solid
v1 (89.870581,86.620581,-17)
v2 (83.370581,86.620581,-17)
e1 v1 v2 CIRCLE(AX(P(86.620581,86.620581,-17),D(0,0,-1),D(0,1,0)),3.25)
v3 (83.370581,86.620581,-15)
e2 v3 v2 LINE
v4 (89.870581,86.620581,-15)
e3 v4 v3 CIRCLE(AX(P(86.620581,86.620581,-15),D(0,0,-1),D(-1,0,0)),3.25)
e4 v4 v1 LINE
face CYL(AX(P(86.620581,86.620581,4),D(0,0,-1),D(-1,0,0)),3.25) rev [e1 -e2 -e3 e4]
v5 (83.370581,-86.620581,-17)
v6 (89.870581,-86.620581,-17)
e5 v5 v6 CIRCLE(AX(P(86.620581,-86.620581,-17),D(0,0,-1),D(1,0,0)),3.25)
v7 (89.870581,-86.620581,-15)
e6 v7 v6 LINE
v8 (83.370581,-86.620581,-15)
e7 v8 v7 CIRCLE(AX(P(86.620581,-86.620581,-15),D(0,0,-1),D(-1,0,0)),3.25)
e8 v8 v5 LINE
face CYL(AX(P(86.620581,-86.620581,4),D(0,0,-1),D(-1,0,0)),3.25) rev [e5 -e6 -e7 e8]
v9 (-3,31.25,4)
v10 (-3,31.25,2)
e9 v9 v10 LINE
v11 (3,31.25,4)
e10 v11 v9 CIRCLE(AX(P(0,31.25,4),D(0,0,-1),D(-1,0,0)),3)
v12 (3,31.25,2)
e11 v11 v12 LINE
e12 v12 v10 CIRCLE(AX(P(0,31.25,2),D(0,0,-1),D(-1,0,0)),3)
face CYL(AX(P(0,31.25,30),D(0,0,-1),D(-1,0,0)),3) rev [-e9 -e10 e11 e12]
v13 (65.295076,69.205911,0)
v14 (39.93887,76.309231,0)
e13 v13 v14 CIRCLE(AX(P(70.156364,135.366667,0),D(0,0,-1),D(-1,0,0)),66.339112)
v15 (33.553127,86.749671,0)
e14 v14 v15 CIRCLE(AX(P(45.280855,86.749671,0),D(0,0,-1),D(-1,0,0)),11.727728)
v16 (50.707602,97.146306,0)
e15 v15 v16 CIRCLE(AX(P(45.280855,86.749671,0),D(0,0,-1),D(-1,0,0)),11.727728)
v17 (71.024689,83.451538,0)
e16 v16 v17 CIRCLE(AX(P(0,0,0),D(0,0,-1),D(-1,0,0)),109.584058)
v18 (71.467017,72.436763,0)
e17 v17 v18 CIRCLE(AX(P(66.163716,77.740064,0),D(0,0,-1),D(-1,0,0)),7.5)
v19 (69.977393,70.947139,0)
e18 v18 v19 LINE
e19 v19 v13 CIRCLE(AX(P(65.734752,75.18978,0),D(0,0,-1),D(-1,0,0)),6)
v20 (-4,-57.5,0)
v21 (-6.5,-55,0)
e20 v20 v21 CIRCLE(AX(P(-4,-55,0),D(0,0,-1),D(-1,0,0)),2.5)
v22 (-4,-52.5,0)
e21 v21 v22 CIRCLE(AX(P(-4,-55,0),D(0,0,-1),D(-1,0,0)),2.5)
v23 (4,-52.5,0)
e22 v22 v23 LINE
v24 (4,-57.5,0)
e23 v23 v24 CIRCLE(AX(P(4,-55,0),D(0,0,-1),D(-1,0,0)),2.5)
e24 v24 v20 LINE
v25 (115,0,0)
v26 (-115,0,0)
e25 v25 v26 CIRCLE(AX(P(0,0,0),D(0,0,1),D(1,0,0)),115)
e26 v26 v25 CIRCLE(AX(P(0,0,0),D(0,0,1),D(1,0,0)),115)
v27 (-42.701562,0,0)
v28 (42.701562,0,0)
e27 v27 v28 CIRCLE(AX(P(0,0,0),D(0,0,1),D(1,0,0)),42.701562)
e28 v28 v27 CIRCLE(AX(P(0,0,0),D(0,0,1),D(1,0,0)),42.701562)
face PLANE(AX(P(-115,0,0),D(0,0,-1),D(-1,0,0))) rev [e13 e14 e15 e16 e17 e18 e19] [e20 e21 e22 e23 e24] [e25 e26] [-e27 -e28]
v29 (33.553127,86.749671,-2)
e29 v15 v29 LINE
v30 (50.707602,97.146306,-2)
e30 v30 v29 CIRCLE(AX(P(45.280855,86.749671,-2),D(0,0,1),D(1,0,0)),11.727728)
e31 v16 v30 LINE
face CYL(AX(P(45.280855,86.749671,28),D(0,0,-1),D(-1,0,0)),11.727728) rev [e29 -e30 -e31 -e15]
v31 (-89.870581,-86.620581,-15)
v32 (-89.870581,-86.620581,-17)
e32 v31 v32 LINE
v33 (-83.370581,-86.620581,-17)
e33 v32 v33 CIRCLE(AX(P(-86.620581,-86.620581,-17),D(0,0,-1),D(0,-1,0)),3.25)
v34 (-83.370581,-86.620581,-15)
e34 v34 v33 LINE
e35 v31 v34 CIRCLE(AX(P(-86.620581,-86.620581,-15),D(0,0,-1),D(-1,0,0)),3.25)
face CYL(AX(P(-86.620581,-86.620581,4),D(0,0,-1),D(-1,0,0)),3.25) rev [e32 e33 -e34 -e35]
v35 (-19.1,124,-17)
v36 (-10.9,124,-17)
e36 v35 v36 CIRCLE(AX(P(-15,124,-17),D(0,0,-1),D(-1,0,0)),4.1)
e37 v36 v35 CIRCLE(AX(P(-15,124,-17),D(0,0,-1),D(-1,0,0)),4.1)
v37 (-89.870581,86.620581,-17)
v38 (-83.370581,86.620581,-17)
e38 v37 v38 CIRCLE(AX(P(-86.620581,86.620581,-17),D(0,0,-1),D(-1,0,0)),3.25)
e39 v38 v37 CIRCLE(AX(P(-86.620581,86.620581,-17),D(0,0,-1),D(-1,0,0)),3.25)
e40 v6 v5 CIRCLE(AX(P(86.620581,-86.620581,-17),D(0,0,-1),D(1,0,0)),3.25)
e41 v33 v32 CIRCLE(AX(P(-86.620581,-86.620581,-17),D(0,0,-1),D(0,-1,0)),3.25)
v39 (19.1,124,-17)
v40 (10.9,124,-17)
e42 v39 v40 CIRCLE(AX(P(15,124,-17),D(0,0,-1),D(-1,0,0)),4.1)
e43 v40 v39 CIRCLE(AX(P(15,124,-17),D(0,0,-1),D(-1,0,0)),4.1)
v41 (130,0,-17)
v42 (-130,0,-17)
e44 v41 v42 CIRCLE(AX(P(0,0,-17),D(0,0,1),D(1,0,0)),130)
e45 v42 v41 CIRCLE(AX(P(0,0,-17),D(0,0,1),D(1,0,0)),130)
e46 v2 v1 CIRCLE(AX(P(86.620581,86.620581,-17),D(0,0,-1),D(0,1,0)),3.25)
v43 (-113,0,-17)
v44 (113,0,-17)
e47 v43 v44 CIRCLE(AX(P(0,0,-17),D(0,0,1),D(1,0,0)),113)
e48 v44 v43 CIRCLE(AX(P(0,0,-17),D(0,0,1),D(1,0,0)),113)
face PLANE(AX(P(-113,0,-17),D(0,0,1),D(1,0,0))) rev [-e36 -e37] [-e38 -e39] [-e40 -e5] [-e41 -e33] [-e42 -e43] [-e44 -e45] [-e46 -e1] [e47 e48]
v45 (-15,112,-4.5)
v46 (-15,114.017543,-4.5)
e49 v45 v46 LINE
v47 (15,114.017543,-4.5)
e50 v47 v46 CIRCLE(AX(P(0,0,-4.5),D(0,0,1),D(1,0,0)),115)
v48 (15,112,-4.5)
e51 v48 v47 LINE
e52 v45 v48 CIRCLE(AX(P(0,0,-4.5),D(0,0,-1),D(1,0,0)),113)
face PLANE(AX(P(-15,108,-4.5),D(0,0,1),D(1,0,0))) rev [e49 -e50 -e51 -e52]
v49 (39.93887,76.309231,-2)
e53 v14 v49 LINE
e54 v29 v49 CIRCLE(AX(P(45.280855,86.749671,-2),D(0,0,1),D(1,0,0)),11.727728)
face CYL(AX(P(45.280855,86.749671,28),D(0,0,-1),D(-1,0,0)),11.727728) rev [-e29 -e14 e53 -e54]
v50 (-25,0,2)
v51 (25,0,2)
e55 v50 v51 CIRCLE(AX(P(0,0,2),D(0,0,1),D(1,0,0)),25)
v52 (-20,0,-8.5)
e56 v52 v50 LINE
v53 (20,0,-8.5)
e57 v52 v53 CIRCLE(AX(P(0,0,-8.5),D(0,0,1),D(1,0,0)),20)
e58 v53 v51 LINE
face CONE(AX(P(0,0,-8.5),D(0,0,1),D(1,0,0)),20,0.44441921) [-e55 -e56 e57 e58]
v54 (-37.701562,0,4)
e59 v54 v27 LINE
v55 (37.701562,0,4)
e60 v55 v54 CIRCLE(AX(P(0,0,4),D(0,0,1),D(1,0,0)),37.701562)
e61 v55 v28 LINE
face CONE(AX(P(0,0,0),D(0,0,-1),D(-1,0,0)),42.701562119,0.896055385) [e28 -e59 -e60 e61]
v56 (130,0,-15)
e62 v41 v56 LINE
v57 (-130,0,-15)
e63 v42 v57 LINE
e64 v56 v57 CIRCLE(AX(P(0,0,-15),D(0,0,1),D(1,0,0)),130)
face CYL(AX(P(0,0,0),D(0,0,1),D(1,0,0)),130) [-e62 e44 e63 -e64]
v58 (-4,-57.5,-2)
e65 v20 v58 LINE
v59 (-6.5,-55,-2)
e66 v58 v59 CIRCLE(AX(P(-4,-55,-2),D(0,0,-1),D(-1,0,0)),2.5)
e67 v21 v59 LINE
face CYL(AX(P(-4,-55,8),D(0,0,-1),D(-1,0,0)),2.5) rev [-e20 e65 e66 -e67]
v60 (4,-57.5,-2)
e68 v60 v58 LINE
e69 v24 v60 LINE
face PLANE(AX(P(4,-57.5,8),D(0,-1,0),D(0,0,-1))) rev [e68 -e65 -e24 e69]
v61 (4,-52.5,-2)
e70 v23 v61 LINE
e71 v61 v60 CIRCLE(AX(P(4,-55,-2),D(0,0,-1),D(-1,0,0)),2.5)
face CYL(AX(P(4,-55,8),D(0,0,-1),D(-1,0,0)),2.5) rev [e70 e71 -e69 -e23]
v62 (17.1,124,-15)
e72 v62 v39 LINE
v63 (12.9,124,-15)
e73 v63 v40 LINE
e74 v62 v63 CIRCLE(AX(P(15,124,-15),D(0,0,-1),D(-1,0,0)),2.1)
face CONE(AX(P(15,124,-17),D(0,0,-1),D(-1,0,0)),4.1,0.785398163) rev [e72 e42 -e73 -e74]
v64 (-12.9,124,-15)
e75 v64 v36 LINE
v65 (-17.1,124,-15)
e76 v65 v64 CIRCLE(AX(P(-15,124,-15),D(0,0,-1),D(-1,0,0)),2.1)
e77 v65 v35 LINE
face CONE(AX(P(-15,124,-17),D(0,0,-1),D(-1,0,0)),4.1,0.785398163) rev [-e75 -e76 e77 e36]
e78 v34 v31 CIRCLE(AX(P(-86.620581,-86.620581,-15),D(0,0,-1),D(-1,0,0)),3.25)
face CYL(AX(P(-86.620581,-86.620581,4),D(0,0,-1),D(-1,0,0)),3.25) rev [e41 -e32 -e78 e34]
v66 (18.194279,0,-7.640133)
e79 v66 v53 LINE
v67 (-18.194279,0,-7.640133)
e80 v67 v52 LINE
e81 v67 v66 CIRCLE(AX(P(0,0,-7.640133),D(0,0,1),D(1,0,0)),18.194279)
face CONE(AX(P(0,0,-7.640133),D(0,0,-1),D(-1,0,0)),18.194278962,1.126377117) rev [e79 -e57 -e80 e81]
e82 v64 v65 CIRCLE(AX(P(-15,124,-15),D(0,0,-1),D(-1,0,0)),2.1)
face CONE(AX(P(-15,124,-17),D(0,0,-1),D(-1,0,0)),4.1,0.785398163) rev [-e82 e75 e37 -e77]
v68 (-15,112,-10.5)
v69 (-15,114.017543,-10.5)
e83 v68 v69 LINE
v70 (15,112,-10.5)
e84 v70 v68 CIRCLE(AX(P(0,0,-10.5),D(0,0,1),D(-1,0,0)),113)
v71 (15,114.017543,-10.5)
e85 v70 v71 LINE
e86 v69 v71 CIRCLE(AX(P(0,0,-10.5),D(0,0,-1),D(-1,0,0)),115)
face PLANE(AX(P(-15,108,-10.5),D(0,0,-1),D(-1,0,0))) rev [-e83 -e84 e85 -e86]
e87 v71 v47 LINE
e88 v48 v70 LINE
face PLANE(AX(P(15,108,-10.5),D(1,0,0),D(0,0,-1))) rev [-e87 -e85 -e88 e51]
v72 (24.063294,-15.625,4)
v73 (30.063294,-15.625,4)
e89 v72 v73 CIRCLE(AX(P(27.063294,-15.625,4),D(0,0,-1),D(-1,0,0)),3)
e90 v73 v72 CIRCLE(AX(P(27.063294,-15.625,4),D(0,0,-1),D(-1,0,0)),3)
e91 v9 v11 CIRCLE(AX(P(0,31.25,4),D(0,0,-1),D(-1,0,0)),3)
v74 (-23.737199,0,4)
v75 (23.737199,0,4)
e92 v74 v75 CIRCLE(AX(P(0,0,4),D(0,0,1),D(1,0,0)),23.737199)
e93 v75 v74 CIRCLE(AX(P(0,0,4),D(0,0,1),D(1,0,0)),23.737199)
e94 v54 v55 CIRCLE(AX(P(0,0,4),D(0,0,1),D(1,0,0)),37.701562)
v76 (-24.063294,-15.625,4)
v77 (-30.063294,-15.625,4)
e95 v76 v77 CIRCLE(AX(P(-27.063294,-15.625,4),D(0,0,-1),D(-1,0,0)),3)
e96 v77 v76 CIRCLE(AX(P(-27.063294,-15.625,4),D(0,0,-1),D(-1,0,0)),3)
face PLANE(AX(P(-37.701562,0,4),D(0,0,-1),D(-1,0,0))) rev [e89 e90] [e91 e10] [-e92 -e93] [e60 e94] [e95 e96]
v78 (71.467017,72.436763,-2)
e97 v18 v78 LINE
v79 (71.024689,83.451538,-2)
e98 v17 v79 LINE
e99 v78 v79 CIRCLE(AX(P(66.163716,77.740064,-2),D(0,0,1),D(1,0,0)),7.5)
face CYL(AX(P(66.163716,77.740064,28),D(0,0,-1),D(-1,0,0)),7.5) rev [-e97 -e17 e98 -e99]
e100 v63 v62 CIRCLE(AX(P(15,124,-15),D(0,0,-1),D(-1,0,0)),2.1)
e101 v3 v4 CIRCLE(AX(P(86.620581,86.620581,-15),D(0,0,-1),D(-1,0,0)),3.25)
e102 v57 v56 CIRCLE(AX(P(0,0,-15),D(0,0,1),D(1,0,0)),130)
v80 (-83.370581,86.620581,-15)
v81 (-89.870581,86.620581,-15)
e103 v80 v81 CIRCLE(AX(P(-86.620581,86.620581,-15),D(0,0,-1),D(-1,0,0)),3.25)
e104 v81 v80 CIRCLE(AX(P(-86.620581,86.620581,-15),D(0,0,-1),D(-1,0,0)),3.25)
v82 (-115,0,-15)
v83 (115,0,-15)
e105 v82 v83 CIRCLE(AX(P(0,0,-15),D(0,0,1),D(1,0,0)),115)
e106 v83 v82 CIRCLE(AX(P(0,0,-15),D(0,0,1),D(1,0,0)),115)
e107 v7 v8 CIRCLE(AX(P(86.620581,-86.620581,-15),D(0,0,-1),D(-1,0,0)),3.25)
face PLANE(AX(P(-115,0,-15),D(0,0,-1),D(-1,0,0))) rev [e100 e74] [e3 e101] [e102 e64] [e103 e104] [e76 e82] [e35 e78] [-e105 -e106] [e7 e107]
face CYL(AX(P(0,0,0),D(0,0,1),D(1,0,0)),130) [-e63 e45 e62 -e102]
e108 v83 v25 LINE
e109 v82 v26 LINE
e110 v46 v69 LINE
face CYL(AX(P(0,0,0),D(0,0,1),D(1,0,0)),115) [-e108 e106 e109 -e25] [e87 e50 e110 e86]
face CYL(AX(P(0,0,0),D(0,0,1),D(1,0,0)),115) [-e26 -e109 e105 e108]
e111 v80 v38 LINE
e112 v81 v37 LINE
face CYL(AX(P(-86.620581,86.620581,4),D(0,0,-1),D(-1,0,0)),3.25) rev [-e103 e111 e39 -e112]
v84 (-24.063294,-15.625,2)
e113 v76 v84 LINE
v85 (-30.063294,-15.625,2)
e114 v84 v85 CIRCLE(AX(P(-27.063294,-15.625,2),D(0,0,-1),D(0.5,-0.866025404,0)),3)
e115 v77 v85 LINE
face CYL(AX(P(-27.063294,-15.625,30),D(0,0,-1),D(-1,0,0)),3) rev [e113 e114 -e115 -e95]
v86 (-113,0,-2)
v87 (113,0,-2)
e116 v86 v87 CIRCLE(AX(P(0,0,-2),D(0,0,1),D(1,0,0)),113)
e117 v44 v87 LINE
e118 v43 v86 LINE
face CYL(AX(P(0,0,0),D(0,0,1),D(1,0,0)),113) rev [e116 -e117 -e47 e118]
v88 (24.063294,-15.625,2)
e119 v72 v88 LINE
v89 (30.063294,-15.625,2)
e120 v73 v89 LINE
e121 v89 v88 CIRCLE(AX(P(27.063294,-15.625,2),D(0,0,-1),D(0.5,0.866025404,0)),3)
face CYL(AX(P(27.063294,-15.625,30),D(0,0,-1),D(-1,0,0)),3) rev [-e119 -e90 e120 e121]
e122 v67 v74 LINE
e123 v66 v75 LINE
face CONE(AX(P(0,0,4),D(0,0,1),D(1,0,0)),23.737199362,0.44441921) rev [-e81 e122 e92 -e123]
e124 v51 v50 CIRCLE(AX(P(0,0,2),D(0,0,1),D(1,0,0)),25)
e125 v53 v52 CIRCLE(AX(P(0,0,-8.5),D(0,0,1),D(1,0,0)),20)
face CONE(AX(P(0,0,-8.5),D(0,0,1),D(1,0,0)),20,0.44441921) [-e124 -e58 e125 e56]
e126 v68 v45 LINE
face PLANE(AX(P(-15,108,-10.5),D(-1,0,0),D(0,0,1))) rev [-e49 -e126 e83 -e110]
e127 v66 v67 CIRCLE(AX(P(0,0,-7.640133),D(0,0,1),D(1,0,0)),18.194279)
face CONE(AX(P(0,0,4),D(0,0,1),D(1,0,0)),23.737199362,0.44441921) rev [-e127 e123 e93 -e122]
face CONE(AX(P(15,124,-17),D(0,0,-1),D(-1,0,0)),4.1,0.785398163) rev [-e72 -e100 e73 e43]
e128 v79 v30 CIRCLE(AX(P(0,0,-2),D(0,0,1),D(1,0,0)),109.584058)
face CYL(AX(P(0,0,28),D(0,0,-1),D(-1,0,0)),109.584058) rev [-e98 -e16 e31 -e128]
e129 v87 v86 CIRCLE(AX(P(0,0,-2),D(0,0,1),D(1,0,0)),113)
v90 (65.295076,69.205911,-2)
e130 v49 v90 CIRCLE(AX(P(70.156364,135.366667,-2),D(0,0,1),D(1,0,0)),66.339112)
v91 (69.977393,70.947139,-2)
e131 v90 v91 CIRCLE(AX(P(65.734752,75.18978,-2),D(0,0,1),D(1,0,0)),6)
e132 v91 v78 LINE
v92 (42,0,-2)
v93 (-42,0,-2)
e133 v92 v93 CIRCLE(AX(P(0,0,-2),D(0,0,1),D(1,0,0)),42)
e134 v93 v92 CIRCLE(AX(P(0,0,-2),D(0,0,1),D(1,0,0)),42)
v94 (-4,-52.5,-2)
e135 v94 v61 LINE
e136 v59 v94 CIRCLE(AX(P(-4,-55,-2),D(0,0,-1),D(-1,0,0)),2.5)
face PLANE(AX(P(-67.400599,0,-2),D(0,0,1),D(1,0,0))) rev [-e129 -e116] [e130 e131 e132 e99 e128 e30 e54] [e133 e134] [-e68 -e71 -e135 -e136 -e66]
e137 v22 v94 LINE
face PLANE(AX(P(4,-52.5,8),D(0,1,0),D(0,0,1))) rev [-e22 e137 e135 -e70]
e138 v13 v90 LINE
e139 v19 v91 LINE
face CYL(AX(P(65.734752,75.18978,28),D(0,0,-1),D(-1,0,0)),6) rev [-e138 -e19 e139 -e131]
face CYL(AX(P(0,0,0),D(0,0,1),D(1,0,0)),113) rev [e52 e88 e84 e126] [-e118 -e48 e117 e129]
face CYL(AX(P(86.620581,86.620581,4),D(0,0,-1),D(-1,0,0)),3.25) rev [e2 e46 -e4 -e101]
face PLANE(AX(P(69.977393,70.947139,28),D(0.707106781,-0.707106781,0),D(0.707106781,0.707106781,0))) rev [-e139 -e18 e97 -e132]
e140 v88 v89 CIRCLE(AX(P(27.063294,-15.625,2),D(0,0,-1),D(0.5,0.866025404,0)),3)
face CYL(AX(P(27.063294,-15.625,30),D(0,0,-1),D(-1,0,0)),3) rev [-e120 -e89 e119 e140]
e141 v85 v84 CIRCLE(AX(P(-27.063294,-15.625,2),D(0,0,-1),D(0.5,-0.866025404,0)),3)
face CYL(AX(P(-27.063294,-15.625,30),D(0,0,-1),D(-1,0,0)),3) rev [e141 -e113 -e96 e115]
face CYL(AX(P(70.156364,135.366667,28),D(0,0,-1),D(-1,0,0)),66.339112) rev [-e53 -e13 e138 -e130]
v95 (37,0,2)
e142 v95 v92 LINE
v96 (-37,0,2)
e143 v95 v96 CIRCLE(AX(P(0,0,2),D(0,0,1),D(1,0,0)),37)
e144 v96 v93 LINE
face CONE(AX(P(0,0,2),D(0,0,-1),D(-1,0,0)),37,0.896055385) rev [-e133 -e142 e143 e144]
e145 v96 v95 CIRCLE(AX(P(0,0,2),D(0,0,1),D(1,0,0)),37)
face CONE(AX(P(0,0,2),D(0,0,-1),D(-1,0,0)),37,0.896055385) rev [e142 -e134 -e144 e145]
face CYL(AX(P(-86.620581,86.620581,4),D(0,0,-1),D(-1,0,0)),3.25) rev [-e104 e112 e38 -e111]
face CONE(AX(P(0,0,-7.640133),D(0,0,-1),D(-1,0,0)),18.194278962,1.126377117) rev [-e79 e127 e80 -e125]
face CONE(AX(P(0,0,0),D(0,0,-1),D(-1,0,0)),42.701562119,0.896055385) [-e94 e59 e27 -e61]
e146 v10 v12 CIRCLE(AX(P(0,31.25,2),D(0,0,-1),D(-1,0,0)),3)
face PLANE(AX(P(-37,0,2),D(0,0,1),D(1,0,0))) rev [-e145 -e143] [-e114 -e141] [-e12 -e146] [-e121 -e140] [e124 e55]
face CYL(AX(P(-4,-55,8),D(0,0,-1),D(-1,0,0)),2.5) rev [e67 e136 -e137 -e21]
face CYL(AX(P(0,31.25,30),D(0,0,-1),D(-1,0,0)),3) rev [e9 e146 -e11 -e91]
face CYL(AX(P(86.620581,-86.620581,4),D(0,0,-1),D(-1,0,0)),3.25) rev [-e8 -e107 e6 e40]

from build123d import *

# Parameters (mm, degrees)
CUT_EXTRUDE1_DEPTH                                   = 45
CUT_EXTRUDE2_DEPTH                                   = 10
SKETCH5_W                                            = 30
SKETCH5_H                                            = 6
CUT_EXTRUDE3_DEPTH                                   = 32
HOLE_SIZE_BY_CROSS_RECESS_COUNTERSUNK_SE_D           = 3.7
HOLE_SIZE_BY_CROSS_RECESS_COUNTERSUNK_SE_CSINK_D     = 8.2
HOLE_SIZE_BY_CROSS_RECESS_COUNTERSUNK_SE_CSINK_ANGLE = 90
SKETCH8_R                                            = 3.25
CUT_EXTRUDE4_DEPTH                                   = 186.04323819
CIRPATTERN1_COUNT                                    = 4
SKETCH9_R                                            = 3
CUT_EXTRUDE5_DEPTH                                   = 28
CIRPATTERN2_COUNT                                    = 3


with BuildPart() as part:
    # Sketch1 → Revolve1 (revolve)
    with BuildSketch(Plane(origin=(0, 0, 0), x_dir=(1, 0, 0), z_dir=(0, 1, 0)), mode=Mode.PRIVATE) as revolve1_sk:
        Polygon((-115, 15), (-130, 15), (-130, 17), (-113, 17), (-113, 2), (-67.400598844, 2), (-42, 2), (-37, -2), (-25, -2), (-20, 8.5), (-18.194278962, 7.640132839), (-23.737199362, -4), (-37.701562119, -4), (-42.701562119, 0), (-115, 0), align=None)
    revolve(revolve1_sk.sketch.rotate(Axis((0, 0, 0), (0, 0, -1)), 180), axis=Axis((0, 0, 0), (0, 0, -1)))

    # Sketch3 → Cut-Extrude1 (cut)
    with BuildSketch(Plane(origin=(0, 0, -17), x_dir=(-1, 0, 0), z_dir=(0, 0, -1))):
        with BuildLine():
            Line((-69.977392836, 70.947139279), (-71.467016668, 72.43676311))
            ThreePointArc((-71.467016668, 72.43676311), (-73.65767572, 78.041003905), (-71.024689008, 83.451538346))
            ThreePointArc((-71.024689008, 83.451538346), (-61.250096658, 90.868538892), (-50.7076021, 97.146306107))
            ThreePointArc((-50.7076021, 97.146306107), (-34.862231231, 92.134081811), (-39.938869953, 76.309230795))
            ThreePointArc((-39.938869953, 76.309230795), (-52.260986787, 71.486832981), (-65.295075938, 69.205911249))
            ThreePointArc((-65.295075938, 69.205911249), (-67.826068353, 69.566044861), (-69.977392836, 70.947139279))
        make_face()
    extrude(amount=-CUT_EXTRUDE1_DEPTH, mode=Mode.SUBTRACT)

    # Sketch4 → Cut-Extrude2 (cut)
    with BuildSketch(Plane(origin=(0, 0, -2), x_dir=(-1, 0, 0), z_dir=(0, 0, -1))):
        with BuildLine():
            Line((-4, -52.5), (4, -52.5))
            ThreePointArc((4, -52.5), (6.5, -55), (4, -57.5))
            Line((4, -57.5), (-4, -57.5))
            ThreePointArc((-4, -57.5), (-6.5, -55), (-4, -52.5))
        make_face()
    extrude(amount=-CUT_EXTRUDE2_DEPTH, mode=Mode.SUBTRACT)

    # Sketch5 → Cut-Extrude3 (cut)
    with BuildSketch(Plane(origin=(0, 140, 0), x_dir=(1, 0, 0), z_dir=(0, 1, 0))):
        with Locations((0, 7.5)):
            Rectangle(SKETCH5_W, SKETCH5_H)
    extrude(amount=-CUT_EXTRUDE3_DEPTH, mode=Mode.SUBTRACT)

    # Hole size by cross-recess countersunk self-tapping screw type1 (through all)
    with Locations(Plane(origin=(15, 124, -17), x_dir=(-1, 0, 0), z_dir=(0, 0, -1))):
        with Locations((0, 0), (30, 0)):
            CounterSinkHole(HOLE_SIZE_BY_CROSS_RECESS_COUNTERSUNK_SE_D / 2, HOLE_SIZE_BY_CROSS_RECESS_COUNTERSUNK_SE_CSINK_D / 2, counter_sink_angle=HOLE_SIZE_BY_CROSS_RECESS_COUNTERSUNK_SE_CSINK_ANGLE)

    # Sketch8 → Cut-Extrude4 (cut, through all)
    with BuildSketch(Plane(origin=(0, 0, -17), x_dir=(-1, 0, 0), z_dir=(0, 0, -1))):
        with Locations((86.620580695, 86.620580695)):
            Circle(SKETCH8_R)
    cut_extrude4 = extrude(amount=-CUT_EXTRUDE4_DEPTH, mode=Mode.SUBTRACT)

    # CirPattern1: Cut-Extrude4 ×4 about axis
    cirpattern1_axis = Axis((0, 0, 0), (0, 0, 1))
    for i in range(1, CIRPATTERN1_COUNT):
        add(cut_extrude4.rotate(cirpattern1_axis, i * 360 / CIRPATTERN1_COUNT), mode=Mode.SUBTRACT)

    # Sketch9 → Cut-Extrude5 (cut)
    with BuildSketch(Plane(origin=(0, 0, 2), x_dir=(-1, 0, 0), z_dir=(0, 0, -1))):
        with Locations((0, 31.25)):
            Circle(SKETCH9_R)
    cut_extrude5 = extrude(amount=-CUT_EXTRUDE5_DEPTH, mode=Mode.SUBTRACT)

    # CirPattern2: Cut-Extrude5 ×3 about axis
    cirpattern2_axis = Axis((0, 0, 0), (0, 0, 1))
    for i in range(1, CIRPATTERN2_COUNT):
        add(cut_extrude5.rotate(cirpattern2_axis, i * 360 / CIRPATTERN2_COUNT), mode=Mode.SUBTRACT)


solid = part.part
